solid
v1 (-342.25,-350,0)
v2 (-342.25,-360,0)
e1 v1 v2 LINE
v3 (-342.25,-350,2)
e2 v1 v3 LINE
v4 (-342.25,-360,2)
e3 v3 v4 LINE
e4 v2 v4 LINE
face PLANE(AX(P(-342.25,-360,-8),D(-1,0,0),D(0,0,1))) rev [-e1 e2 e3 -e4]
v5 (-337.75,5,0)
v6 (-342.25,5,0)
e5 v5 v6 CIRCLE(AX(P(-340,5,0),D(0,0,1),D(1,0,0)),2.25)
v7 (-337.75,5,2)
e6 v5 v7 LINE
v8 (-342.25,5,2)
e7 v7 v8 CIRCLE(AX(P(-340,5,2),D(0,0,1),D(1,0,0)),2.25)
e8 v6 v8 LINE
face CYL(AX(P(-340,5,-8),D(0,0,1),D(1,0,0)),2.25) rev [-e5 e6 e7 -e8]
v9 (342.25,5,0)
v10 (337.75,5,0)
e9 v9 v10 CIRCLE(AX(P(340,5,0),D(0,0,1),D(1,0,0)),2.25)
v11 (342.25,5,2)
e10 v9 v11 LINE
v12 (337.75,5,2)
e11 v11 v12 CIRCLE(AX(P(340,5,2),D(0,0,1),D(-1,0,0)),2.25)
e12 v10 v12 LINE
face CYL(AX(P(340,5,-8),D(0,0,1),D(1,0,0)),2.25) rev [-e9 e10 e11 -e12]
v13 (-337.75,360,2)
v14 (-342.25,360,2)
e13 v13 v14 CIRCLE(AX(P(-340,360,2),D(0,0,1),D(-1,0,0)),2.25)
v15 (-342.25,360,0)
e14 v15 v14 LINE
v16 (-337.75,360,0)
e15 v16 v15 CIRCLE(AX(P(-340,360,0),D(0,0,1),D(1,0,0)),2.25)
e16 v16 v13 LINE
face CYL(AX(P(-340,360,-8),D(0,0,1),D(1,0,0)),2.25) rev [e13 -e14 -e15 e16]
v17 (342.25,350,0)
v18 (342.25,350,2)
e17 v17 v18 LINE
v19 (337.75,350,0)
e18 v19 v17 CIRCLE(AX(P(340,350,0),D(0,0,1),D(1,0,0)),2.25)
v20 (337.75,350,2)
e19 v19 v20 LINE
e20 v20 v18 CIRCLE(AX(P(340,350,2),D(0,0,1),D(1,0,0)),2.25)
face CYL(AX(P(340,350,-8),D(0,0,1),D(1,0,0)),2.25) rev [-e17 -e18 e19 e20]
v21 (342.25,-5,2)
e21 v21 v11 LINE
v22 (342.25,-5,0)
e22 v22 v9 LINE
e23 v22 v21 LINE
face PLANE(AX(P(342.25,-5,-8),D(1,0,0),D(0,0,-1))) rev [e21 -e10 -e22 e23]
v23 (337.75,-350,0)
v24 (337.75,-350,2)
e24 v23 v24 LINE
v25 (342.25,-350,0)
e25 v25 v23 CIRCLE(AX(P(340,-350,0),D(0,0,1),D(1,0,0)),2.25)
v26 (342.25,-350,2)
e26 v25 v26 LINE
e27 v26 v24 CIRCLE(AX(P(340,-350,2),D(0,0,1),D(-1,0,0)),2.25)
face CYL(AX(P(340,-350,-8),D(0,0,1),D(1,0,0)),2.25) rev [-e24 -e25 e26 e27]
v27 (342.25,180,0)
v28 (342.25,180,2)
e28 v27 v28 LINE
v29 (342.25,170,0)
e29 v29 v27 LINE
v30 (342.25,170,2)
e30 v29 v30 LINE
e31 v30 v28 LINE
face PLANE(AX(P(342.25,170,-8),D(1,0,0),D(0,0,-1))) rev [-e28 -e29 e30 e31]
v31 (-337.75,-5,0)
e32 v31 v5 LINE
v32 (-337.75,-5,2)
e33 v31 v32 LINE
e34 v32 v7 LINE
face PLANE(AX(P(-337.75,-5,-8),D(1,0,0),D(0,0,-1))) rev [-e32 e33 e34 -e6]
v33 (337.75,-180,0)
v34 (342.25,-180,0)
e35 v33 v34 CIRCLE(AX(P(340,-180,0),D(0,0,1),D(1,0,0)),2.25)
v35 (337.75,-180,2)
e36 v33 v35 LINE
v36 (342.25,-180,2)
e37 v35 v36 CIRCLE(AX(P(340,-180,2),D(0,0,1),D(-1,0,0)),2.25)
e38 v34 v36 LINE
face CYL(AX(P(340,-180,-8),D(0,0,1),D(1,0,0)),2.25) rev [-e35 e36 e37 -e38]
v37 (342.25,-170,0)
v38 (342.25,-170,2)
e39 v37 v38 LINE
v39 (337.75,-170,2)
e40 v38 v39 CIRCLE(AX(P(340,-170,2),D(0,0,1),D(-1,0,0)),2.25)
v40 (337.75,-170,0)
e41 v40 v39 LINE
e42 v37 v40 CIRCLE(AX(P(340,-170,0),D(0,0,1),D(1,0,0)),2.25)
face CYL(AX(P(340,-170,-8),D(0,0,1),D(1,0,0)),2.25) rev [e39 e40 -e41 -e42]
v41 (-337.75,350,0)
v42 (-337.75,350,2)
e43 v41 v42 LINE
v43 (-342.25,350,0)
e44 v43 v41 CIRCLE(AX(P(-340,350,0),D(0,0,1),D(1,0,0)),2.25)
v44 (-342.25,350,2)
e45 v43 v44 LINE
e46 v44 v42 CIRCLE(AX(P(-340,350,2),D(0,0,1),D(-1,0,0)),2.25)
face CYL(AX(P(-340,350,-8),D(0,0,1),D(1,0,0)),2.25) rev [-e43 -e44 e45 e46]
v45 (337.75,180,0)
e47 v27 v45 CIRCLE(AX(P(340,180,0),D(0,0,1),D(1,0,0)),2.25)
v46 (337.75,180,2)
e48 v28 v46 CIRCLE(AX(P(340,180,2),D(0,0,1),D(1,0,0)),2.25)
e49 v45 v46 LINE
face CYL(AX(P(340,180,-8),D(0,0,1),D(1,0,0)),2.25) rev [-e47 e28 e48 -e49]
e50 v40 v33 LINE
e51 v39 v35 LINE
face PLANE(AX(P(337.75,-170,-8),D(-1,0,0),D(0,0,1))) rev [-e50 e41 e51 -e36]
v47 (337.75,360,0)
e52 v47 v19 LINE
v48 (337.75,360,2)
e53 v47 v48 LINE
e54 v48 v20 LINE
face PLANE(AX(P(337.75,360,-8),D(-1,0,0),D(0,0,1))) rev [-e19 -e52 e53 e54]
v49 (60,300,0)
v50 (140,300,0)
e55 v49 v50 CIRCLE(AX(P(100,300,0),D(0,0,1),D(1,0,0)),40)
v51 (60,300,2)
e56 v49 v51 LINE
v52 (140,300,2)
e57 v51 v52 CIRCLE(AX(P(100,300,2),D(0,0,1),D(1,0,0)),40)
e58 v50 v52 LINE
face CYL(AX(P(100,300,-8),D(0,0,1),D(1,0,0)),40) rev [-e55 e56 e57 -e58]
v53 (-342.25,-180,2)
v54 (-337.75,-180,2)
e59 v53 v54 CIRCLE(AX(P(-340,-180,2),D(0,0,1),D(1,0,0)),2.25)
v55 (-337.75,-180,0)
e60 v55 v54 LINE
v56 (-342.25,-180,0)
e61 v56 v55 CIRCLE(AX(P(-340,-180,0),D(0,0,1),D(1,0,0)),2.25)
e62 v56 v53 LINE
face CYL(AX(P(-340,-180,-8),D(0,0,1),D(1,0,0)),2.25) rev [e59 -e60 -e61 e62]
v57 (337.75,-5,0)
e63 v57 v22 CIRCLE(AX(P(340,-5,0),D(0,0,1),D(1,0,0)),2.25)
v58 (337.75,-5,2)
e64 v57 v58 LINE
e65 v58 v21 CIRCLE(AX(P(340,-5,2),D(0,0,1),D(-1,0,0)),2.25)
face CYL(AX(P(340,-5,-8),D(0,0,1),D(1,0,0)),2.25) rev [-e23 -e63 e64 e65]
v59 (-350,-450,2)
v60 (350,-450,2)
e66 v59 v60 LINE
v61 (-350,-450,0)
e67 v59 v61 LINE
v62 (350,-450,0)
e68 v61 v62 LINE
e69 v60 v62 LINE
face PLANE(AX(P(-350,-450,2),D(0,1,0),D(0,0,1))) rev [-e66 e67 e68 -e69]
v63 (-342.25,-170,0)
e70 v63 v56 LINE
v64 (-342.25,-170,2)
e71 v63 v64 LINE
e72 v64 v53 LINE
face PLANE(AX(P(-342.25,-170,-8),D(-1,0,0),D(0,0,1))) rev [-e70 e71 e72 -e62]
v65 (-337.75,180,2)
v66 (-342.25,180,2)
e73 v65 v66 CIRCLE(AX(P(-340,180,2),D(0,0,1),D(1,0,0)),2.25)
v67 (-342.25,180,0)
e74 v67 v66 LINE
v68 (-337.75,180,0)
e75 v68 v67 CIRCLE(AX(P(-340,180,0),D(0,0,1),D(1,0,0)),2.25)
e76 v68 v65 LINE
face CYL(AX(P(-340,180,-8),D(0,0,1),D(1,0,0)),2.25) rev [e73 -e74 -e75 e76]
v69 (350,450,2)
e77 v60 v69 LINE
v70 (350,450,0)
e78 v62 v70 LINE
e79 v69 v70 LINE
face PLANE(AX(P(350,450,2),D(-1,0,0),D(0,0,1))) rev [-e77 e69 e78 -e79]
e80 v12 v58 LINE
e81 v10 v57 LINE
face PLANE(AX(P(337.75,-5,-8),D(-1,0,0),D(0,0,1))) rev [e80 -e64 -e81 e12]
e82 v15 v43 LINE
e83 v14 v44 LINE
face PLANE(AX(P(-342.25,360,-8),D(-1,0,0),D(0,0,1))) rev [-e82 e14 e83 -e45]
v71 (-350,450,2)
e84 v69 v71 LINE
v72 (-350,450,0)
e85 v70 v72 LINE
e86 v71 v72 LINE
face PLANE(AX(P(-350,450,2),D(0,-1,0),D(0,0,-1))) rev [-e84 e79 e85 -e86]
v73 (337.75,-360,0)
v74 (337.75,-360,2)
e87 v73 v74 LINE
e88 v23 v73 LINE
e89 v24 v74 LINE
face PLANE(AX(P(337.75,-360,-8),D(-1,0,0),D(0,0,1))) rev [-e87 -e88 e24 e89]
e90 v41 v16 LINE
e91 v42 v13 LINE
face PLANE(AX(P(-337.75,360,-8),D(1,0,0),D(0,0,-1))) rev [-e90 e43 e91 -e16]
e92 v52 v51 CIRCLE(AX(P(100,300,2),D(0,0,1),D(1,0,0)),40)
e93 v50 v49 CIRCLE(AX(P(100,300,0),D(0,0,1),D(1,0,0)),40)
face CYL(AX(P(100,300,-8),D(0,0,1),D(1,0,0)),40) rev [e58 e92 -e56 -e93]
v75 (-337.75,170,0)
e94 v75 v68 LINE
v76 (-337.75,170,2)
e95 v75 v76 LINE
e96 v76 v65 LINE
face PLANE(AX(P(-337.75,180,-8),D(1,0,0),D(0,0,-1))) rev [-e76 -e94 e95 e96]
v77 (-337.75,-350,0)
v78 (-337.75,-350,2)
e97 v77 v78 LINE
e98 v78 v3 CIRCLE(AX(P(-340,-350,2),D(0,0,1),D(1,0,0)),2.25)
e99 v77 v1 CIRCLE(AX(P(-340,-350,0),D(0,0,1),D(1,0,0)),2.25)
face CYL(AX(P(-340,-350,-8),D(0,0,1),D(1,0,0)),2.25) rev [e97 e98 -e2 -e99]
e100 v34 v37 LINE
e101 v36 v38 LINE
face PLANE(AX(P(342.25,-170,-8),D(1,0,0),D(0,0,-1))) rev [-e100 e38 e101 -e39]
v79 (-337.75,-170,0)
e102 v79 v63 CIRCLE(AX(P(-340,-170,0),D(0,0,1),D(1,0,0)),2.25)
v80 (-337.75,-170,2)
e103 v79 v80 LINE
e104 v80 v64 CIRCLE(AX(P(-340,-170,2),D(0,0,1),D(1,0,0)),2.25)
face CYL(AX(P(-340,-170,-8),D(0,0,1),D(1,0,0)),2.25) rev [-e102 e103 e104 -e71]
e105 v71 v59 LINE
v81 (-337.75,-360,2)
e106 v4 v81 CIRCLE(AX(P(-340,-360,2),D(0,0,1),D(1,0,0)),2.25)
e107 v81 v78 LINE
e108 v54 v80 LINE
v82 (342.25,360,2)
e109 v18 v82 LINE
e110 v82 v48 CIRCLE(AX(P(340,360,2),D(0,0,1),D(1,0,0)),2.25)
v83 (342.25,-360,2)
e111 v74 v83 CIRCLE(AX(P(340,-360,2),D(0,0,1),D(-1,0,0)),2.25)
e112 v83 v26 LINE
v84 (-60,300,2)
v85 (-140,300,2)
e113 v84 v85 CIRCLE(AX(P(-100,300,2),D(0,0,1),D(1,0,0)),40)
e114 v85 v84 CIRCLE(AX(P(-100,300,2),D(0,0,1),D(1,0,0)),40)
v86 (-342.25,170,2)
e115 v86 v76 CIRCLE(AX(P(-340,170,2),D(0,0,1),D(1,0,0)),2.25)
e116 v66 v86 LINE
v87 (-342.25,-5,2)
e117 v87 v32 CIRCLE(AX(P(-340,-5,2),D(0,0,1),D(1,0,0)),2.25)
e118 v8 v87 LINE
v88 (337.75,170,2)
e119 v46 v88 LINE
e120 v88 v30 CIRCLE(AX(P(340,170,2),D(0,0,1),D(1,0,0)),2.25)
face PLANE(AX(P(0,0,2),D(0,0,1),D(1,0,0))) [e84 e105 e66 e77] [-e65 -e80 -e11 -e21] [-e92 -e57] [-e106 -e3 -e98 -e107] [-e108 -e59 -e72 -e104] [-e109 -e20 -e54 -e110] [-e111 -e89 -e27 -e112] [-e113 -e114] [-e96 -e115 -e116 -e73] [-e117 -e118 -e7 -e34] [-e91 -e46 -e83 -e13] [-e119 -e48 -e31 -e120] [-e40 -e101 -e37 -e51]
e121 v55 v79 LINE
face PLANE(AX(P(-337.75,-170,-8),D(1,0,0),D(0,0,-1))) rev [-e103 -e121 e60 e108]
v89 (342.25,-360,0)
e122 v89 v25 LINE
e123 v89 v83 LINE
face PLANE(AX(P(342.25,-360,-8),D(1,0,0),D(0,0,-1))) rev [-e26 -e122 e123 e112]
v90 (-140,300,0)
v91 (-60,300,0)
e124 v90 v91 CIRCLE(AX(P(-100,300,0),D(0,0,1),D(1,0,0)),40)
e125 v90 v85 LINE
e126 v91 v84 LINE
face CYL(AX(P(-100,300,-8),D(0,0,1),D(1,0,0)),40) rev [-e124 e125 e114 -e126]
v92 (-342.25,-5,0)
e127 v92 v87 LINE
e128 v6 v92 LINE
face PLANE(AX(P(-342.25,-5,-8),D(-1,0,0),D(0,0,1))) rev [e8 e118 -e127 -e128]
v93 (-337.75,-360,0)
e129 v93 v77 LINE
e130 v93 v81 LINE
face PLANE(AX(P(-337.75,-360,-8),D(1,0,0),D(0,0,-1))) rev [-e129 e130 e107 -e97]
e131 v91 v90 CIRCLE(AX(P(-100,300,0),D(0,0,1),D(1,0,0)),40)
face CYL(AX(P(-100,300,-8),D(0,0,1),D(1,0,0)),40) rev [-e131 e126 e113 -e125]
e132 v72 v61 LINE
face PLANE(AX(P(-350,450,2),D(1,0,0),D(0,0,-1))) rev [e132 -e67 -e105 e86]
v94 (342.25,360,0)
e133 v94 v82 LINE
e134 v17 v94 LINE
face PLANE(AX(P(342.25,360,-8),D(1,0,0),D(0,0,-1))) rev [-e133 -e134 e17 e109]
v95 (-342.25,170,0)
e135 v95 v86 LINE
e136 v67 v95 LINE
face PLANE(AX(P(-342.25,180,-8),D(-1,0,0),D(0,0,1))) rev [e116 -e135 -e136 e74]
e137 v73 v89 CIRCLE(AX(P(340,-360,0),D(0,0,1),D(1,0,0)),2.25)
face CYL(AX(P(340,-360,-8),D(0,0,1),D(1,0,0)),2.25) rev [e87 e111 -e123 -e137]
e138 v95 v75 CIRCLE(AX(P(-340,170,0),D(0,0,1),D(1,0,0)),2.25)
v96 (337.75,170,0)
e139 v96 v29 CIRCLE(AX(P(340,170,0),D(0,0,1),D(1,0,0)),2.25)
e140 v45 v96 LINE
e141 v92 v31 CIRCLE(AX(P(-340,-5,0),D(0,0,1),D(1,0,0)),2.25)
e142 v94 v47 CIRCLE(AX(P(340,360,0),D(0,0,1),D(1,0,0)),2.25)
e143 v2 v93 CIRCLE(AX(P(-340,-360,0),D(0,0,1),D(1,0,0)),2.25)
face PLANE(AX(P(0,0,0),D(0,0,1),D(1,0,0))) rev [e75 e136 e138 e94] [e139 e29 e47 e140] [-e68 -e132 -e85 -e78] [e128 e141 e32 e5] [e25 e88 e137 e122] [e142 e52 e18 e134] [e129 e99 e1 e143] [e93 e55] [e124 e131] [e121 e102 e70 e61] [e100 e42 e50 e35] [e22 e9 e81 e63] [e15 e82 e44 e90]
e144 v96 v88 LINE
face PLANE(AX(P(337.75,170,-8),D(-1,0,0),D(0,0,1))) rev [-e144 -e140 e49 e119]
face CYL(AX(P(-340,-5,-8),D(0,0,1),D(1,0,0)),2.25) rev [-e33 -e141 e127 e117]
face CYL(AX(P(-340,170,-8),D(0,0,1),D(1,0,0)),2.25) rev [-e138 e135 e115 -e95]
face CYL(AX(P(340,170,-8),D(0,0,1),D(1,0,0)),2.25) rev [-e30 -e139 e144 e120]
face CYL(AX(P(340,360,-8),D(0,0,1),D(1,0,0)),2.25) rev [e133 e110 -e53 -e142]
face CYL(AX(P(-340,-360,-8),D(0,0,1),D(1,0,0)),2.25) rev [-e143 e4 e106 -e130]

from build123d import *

# Parameters (mm, degrees)
SKETCH_1_W          = 700
SKETCH_1_H          = 900
EXTRUDE_1_DEPTH     = 2
CUT_EXTRUDE_1_DEPTH = 10
SKETCH_3_R          = 40
CUT_EXTRUDE_2_DEPTH = 10


with BuildPart() as part:
    # 草图1 → 凸台-拉伸1 (new body)
    with BuildSketch(Plane.XY):
        Rectangle(SKETCH_1_W, SKETCH_1_H)
    extrude(amount=EXTRUDE_1_DEPTH)

    # 草图2 → 切除-拉伸1 (cut)
    with BuildSketch(Plane.XY.offset(2)):
        with BuildLine():
            Line((-337.75, 180), (-337.75, 170))
            ThreePointArc((-337.75, 170), (-340, 167.75), (-342.25, 170))
            Line((-342.25, 170), (-342.25, 180))
            ThreePointArc((-342.25, 180), (-340, 182.25), (-337.75, 180))
        make_face()
        with BuildLine():
            Line((-342.25, -5), (-342.25, 5))
            ThreePointArc((-342.25, 5), (-340, 7.25), (-337.75, 5))
            Line((-337.75, 5), (-337.75, -5))
            ThreePointArc((-337.75, -5), (-340, -7.25), (-342.25, -5))
        make_face()
        with BuildLine():
            Line((337.75, 170), (337.75, 180))
            ThreePointArc((337.75, 180), (340, 182.25), (342.25, 180))
            Line((342.25, 180), (342.25, 170))
            ThreePointArc((342.25, 170), (340, 167.75), (337.75, 170))
        make_face()
        with BuildLine():
            Line((342.25, -5), (342.25, 5))
            ThreePointArc((342.25, 5), (340, 7.25), (337.75, 5))
            Line((337.75, 5), (337.75, -5))
            ThreePointArc((337.75, -5), (340, -7.25), (342.25, -5))
        make_face()
        with BuildLine():
            Line((-342.25, 360), (-342.25, 350))
            ThreePointArc((-342.25, 350), (-340, 347.75), (-337.75, 350))
            Line((-337.75, 350), (-337.75, 360))
            ThreePointArc((-337.75, 360), (-340, 362.25), (-342.25, 360))
        make_face()
        with BuildLine():
            Line((337.75, -170), (337.75, -180))
            ThreePointArc((337.75, -180), (340, -182.25), (342.25, -180))
            Line((342.25, -180), (342.25, -170))
            ThreePointArc((342.25, -170), (340, -167.75), (337.75, -170))
        make_face()
        with BuildLine():
            Line((342.25, 360), (342.25, 350))
            ThreePointArc((342.25, 350), (340, 347.75), (337.75, 350))
            Line((337.75, 350), (337.75, 360))
            ThreePointArc((337.75, 360), (340, 362.25), (342.25, 360))
        make_face()
        with BuildLine():
            Line((342.25, -360), (342.25, -350))
            ThreePointArc((342.25, -350), (340, -347.75), (337.75, -350))
            Line((337.75, -350), (337.75, -360))
            ThreePointArc((337.75, -360), (340, -362.25), (342.25, -360))
        make_face()
        with BuildLine():
            Line((-342.25, -360), (-342.25, -350))
            ThreePointArc((-342.25, -350), (-340, -347.75), (-337.75, -350))
            Line((-337.75, -350), (-337.75, -360))
            ThreePointArc((-337.75, -360), (-340, -362.25), (-342.25, -360))
        make_face()
        with BuildLine():
            Line((-337.75, -170), (-337.75, -180))
            ThreePointArc((-337.75, -180), (-340, -182.25), (-342.25, -180))
            Line((-342.25, -180), (-342.25, -170))
            ThreePointArc((-342.25, -170), (-340, -167.75), (-337.75, -170))
        make_face()
    extrude(amount=-CUT_EXTRUDE_1_DEPTH, mode=Mode.SUBTRACT)

    # 草图3 → 切除-拉伸2 (cut)
    with BuildSketch(Plane.XY.offset(2)):
        with Locations((-100, 300)):
            Circle(SKETCH_3_R)
        with Locations((100, 300)):
            Circle(SKETCH_3_R)
    extrude(amount=-CUT_EXTRUDE_2_DEPTH, mode=Mode.SUBTRACT)


solid = part.part
